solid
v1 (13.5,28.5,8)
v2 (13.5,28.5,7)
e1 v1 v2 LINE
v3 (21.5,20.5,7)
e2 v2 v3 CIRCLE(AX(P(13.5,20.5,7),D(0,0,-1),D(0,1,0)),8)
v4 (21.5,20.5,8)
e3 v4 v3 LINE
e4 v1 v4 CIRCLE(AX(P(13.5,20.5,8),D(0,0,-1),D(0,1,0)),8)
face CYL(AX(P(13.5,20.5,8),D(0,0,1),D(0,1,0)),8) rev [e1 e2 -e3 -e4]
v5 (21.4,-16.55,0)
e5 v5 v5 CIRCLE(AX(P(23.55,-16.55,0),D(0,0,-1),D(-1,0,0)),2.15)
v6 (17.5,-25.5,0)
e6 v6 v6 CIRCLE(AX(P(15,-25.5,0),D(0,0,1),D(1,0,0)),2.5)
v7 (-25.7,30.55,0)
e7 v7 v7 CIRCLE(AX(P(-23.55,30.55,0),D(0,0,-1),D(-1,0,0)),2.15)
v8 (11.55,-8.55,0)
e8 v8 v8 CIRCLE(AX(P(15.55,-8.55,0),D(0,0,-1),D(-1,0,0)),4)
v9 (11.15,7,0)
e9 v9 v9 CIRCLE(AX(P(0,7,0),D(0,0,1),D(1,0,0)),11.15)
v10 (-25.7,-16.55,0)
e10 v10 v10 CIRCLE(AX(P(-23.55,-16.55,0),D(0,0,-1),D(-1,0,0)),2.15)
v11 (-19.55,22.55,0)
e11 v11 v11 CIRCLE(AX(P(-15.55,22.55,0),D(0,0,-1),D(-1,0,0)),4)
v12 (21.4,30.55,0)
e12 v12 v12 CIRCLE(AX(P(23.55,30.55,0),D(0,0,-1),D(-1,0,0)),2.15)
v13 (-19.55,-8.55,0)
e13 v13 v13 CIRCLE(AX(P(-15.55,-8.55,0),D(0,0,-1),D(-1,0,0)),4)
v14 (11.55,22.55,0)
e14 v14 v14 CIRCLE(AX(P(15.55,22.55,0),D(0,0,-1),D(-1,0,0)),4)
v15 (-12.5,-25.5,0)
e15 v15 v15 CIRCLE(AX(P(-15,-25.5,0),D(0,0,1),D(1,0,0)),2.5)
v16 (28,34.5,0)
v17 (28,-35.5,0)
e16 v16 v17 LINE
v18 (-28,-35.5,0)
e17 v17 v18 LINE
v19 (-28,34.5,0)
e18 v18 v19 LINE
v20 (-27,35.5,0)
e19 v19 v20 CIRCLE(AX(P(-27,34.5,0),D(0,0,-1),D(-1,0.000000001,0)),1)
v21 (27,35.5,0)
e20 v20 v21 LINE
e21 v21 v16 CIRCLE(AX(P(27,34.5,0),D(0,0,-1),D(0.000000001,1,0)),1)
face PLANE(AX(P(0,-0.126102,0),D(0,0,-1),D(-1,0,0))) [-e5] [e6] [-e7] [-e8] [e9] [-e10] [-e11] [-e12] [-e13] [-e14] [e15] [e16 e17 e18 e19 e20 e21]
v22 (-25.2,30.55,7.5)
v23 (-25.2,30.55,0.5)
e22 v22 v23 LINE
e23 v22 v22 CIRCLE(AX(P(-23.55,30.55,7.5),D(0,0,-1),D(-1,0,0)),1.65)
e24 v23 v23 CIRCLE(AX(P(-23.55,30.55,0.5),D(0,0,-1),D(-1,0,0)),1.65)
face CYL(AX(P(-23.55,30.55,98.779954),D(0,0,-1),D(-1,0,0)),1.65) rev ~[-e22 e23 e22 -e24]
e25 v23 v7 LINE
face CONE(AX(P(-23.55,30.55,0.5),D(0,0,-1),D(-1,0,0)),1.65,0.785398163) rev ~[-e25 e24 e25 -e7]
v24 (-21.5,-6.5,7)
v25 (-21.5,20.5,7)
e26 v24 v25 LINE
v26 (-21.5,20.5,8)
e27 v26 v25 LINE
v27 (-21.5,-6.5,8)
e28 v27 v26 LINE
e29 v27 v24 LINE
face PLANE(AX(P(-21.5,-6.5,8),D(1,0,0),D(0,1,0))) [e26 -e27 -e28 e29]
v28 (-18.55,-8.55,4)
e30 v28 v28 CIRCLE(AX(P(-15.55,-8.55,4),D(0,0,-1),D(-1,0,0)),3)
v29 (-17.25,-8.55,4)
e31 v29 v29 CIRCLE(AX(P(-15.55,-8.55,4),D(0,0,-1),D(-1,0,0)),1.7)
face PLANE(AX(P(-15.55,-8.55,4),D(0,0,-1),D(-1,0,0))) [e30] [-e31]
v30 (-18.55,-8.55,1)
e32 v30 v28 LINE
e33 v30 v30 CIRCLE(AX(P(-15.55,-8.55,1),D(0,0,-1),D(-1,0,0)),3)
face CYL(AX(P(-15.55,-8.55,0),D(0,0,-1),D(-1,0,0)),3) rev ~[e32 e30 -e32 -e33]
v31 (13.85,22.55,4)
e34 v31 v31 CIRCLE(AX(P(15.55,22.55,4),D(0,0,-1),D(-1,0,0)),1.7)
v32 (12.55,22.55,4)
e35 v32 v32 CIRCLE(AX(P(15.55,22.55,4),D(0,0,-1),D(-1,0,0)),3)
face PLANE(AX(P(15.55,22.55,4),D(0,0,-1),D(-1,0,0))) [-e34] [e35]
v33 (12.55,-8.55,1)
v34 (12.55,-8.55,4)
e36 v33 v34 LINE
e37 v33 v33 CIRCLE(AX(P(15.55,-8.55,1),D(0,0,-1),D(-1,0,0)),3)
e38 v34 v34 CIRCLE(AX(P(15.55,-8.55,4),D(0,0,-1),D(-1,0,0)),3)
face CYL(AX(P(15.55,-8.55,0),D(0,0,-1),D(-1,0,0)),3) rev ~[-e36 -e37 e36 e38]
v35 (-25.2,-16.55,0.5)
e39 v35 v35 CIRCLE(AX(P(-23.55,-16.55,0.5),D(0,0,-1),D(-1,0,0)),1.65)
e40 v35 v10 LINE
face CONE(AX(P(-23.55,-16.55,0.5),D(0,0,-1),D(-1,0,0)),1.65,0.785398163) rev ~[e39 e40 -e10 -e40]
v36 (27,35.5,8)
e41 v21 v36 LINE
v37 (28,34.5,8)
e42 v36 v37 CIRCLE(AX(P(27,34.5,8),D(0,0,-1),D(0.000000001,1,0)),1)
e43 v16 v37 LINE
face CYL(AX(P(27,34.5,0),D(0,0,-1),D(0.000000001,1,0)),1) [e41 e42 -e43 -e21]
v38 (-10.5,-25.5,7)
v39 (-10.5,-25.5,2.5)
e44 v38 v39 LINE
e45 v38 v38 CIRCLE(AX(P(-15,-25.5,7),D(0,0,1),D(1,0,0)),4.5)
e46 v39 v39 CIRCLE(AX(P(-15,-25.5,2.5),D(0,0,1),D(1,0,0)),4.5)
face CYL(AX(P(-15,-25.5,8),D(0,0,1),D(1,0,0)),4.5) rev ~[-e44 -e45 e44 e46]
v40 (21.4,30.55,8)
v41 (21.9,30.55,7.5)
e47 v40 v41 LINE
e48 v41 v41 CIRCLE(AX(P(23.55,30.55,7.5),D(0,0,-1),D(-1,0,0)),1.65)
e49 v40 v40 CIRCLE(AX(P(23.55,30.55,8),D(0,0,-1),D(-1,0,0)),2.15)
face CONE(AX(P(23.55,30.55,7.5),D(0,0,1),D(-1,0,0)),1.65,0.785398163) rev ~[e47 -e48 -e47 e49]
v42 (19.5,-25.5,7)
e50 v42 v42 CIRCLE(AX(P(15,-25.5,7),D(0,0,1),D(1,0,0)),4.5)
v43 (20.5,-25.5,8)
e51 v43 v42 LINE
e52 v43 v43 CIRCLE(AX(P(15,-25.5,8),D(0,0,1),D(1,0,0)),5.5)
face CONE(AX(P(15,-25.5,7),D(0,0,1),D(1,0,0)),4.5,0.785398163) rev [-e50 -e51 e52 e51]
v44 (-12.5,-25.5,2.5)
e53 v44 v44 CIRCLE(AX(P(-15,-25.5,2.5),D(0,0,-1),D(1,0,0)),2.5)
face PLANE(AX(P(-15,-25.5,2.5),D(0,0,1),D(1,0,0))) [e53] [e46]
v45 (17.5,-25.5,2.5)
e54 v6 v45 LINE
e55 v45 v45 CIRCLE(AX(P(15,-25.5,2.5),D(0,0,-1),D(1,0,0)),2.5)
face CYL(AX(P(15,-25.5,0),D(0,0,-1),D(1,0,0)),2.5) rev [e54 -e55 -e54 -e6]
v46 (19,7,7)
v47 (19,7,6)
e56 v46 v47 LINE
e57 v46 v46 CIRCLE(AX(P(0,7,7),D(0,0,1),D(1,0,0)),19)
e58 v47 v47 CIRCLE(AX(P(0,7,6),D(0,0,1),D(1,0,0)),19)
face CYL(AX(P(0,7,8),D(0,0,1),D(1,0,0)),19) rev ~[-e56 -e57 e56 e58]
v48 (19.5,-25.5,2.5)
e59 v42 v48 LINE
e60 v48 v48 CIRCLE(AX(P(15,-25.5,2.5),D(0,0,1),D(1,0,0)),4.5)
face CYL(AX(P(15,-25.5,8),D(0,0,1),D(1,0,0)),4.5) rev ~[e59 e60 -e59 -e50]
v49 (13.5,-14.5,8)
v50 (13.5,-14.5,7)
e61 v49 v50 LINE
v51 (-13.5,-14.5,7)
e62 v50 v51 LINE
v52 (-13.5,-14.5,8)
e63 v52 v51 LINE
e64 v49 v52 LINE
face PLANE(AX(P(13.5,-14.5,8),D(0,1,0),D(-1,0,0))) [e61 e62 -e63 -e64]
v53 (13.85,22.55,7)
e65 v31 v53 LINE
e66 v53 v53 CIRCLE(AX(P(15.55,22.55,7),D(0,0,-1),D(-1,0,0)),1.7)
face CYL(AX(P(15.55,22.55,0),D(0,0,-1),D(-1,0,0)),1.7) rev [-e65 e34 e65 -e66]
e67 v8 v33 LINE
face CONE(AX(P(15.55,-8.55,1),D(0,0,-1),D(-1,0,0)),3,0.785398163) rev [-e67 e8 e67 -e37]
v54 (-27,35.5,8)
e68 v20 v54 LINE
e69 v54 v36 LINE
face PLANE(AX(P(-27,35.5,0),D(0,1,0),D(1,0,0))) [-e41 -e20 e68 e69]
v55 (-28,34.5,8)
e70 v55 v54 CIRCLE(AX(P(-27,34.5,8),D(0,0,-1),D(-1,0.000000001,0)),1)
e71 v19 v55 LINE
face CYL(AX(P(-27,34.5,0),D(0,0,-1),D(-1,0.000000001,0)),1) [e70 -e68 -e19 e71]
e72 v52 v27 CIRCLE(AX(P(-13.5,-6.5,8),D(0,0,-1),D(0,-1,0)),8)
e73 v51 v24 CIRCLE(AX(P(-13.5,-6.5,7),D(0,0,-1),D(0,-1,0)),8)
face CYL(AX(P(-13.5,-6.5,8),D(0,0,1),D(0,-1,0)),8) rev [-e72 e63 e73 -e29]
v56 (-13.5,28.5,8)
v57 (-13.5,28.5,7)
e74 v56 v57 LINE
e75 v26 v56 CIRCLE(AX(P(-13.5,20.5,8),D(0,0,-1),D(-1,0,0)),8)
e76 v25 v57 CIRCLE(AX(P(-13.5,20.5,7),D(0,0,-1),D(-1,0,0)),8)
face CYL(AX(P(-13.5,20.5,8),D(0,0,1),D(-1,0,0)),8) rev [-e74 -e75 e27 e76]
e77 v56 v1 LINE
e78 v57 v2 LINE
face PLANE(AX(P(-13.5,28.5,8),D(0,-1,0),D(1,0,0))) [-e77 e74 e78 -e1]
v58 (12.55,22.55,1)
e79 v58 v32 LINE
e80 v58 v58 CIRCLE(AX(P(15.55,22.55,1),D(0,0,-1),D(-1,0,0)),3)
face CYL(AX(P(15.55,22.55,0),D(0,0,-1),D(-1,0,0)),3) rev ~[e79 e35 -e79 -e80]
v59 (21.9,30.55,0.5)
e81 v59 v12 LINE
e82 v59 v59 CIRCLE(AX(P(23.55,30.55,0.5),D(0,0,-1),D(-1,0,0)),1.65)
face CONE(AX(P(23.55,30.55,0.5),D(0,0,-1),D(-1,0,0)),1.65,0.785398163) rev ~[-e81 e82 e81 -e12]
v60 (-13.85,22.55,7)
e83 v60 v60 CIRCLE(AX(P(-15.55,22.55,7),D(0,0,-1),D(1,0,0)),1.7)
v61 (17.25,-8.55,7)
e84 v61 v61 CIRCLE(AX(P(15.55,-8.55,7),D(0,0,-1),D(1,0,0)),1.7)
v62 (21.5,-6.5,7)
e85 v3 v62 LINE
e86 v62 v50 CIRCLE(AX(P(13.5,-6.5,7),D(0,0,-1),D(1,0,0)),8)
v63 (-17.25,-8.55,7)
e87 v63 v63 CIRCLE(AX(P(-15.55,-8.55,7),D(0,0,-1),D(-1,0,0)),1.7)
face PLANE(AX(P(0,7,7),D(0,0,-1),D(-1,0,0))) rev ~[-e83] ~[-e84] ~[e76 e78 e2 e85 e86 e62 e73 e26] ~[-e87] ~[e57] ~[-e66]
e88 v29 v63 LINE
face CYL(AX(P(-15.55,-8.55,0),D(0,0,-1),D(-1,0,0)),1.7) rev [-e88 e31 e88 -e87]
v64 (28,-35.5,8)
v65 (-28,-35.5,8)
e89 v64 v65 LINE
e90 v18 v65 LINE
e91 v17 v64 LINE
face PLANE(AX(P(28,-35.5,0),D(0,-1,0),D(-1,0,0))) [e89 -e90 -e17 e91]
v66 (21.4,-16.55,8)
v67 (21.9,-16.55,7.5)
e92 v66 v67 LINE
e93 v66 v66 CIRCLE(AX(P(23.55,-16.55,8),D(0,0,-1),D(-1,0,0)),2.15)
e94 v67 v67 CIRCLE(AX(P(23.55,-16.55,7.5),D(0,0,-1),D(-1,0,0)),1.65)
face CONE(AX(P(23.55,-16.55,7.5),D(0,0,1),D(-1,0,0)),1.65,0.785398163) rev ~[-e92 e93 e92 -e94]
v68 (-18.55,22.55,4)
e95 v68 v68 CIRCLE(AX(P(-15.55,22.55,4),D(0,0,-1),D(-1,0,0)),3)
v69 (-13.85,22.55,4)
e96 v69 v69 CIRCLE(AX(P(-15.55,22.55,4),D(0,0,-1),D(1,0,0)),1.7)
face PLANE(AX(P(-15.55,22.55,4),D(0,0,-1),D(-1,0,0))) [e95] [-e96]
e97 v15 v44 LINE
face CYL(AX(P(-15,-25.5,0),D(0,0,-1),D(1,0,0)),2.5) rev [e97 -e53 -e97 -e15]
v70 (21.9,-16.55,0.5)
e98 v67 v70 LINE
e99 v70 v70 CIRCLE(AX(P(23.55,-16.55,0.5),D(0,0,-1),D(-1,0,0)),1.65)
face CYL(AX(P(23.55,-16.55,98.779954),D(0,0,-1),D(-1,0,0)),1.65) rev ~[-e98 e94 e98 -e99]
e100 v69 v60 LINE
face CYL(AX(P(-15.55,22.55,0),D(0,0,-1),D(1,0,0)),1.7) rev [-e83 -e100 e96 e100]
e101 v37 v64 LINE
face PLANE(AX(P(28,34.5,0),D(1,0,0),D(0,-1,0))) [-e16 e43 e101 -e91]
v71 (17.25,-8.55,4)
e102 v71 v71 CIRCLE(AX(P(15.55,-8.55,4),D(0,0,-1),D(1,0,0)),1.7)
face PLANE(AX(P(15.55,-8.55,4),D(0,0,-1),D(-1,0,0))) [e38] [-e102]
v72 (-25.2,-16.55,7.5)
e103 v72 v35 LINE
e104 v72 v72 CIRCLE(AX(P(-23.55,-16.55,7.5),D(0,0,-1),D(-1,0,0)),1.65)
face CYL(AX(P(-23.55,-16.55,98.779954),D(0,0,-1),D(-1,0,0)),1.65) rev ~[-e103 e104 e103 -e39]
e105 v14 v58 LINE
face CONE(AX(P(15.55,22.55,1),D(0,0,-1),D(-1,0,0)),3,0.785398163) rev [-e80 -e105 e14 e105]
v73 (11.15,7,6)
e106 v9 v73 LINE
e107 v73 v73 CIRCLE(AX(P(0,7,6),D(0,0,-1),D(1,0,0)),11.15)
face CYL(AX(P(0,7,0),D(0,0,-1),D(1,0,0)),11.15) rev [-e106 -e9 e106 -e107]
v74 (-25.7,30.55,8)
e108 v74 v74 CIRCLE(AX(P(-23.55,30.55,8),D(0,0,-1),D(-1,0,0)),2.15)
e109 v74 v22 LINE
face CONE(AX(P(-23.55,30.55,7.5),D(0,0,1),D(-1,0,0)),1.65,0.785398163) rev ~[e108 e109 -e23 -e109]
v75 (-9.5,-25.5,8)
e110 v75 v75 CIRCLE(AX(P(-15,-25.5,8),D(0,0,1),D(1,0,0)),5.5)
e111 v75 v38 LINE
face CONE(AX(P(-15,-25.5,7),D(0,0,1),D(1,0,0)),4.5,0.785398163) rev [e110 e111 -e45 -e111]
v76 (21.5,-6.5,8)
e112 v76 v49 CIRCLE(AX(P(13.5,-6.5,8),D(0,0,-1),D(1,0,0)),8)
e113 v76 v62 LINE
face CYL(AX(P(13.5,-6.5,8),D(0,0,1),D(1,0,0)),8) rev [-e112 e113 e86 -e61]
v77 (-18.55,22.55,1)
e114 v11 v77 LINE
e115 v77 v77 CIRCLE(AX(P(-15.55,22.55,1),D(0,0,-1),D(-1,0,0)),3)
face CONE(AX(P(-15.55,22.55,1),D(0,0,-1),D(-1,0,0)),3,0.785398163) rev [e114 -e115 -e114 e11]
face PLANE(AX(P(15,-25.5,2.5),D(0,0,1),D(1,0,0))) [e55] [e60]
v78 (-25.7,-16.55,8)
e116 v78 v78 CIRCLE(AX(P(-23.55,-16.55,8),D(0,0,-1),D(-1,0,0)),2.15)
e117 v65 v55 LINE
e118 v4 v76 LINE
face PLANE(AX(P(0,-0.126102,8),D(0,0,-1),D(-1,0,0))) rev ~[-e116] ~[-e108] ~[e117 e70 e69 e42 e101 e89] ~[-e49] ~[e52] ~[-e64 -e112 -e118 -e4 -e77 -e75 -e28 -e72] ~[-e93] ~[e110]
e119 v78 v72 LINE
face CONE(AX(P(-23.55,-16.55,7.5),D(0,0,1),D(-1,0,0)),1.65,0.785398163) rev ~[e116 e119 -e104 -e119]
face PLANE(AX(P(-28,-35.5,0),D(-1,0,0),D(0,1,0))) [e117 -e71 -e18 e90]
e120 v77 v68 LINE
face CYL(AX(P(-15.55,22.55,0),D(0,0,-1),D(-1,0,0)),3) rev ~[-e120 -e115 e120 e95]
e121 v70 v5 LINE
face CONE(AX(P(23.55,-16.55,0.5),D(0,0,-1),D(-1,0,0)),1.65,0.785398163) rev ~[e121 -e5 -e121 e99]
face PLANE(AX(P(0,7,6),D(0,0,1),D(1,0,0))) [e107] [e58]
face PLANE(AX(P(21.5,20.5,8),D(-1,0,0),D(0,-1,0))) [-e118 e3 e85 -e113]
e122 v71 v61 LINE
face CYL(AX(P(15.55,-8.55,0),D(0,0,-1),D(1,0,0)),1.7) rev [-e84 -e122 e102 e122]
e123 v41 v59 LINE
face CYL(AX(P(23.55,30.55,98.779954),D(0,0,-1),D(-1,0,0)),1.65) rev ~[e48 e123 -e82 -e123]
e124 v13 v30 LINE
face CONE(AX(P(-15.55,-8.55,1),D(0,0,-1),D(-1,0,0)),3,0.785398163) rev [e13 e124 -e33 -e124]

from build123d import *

# Parameters (mm, degrees)
SKETCH1_R           = 11.15
SKETCH1_R_2         = 1.7
SKETCH1_R_3         = 1
SKETCH1_R_4         = 2.5
BOSS_EXTRUDE1_DEPTH = 8
SKETCH2_R           = 4.5
CUT_EXTRUDE1_DEPTH  = 5.5
SKETCH3_R           = 3
CUT_EXTRUDE2_DEPTH  = 4
CHAMFER1_SIZE       = 1
CHAMFER2_SIZE       = 0.5
CHAMFER3_SIZE       = 0.5
SKETCH4_R           = 19
CUT_EXTRUDE3_DEPTH  = 2
CUT_EXTRUDE4_DEPTH  = 1
CHAMFER4_SIZE       = 1
M4_TAPPED_HOLE1_D   = 3.3
CHAMFER5_SIZE       = 0.5


with BuildPart() as part:
    # Sketch1 → Boss-Extrude1 (new body)
    with BuildSketch(Plane.XY):
        with BuildLine():
            Line((-27, 35.5), (27, 35.5))
            ThreePointArc((27, 35.5), (27.707106781, 35.207106781), (28, 34.5))
            Line((28, 34.5), (28, -35.5))
            Line((28, -35.5), (-28, -35.5))
            Line((-28, -35.5), (-28, 34.5))
            ThreePointArc((-28, 34.5), (-27.707106781, 35.207106781), (-27, 35.5))
        make_face()
        with Locations((0, 7)):
            Circle(SKETCH1_R, mode=Mode.SUBTRACT)
        with Locations((-15.55, 22.55)):
            Circle(SKETCH1_R_2, mode=Mode.SUBTRACT)
        with Locations((-23.55, 30.55)):
            Circle(SKETCH1_R_3, mode=Mode.SUBTRACT)
        with Locations(Location((23.55, 30.55, 0), (0, 0, 180))):
            Circle(SKETCH1_R_3, mode=Mode.SUBTRACT)
        with Locations(Location((15.55, 22.55, 0), (0, 0, 180))):
            Circle(SKETCH1_R_2, mode=Mode.SUBTRACT)
        with Locations(Location((-23.55, -16.55, 0), (0, 0, 180))):
            Circle(SKETCH1_R_3, mode=Mode.SUBTRACT)
        with Locations(Location((-15.55, -8.55, 0), (0, 0, 180))):
            Circle(SKETCH1_R_2, mode=Mode.SUBTRACT)
        with Locations((15.55, -8.55)):
            Circle(SKETCH1_R_2, mode=Mode.SUBTRACT)
        with Locations((23.55, -16.55)):
            Circle(SKETCH1_R_3, mode=Mode.SUBTRACT)
        with Locations((-15, -25.5)):
            Circle(SKETCH1_R_4, mode=Mode.SUBTRACT)
        with Locations((15, -25.5)):
            Circle(SKETCH1_R_4, mode=Mode.SUBTRACT)
    extrude(amount=BOSS_EXTRUDE1_DEPTH)

    # Sketch2 → Cut-Extrude1 (cut)
    with BuildSketch(Plane.XY.offset(8)):
        with Locations((-15, -25.5)):
            Circle(SKETCH2_R)
        with Locations((15, -25.5)):
            Circle(SKETCH2_R)
    extrude(amount=-CUT_EXTRUDE1_DEPTH, mode=Mode.SUBTRACT)

    # Sketch3 → Cut-Extrude2 (cut)
    with BuildSketch(Plane(origin=(0, 0, 0), x_dir=(-1, 0, 0), z_dir=(0, 0, -1))):
        with Locations((-15.55, 22.55)):
            Circle(SKETCH3_R)
        with Locations((15.55, 22.55)):
            Circle(SKETCH3_R)
        with Locations((-15.55, -8.55)):
            Circle(SKETCH3_R)
        with Locations((15.55, -8.55)):
            Circle(SKETCH3_R)
    extrude(amount=-CUT_EXTRUDE2_DEPTH, mode=Mode.SUBTRACT)

    # Chamfer1
    chamfer1_edges = [part.edges().sort_by_distance(p)[0] for p in [
        (18.55, 22.55, 0),
        (-12.55, 22.55, 0),
        (18.55, -8.55, 0),
        (-12.55, -8.55, 0),
    ]]
    chamfer(chamfer1_edges, length=CHAMFER1_SIZE)

    # Chamfer2
    chamfer2_edges = [part.edges().sort_by_distance(p)[0] for p in [
        (-24.55, 30.55, 0),
        (24.55, 30.55, 0),
        (-22.55, -16.55, 0),
        (22.55, -16.55, 0),
    ]]
    chamfer(chamfer2_edges, length=CHAMFER2_SIZE)

    # Chamfer3
    chamfer3_edges = [part.edges().sort_by_distance(p)[0] for p in [
        (-24.55, 30.55, 8),
        (24.55, 30.55, 8),
        (-22.55, -16.55, 8),
        (22.55, -16.55, 8),
    ]]
    chamfer(chamfer3_edges, length=CHAMFER3_SIZE)

    # Sketch4 → Cut-Extrude3 (cut)
    with BuildSketch(Plane.XY.offset(8)):
        with Locations((0, 7)):
            Circle(SKETCH4_R)
    extrude(amount=-CUT_EXTRUDE3_DEPTH, mode=Mode.SUBTRACT)

    # Sketch5 → Cut-Extrude4 (cut)
    with BuildSketch(Plane.XY.offset(8)):
        with BuildLine():
            Line((-13.5, 28.5), (13.5, 28.5))
            ThreePointArc((13.5, 28.5), (19.156854249, 26.156854249), (21.5, 20.5))
            Line((21.5, 20.5), (21.5, -6.5))
            ThreePointArc((21.5, -6.5), (19.156854249, -12.156854249), (13.5, -14.5))
            Line((13.5, -14.5), (-13.5, -14.5))
            ThreePointArc((-13.5, -14.5), (-19.156854249, -12.156854249), (-21.5, -6.5))
            Line((-21.5, -6.5), (-21.5, 20.5))
            ThreePointArc((-21.5, 20.5), (-19.156854249, 26.156854249), (-13.5, 28.5))
        make_face()
    extrude(amount=-CUT_EXTRUDE4_DEPTH, mode=Mode.SUBTRACT)

    # Chamfer4
    chamfer4_edges = [part.edges().sort_by_distance(p)[0] for p in [
        (-19.5, -25.5, 8),
        (10.5, -25.5, 8),
    ]]
    chamfer(chamfer4_edges, length=CHAMFER4_SIZE)

    # M4 Tapped Hole1 (through all)
    with Locations(Plane.XY.offset(8)):
        with Locations((-23.55, 30.55), (23.55, 30.55), (23.55, -16.55), (-23.55, -16.55)):
            Hole(M4_TAPPED_HOLE1_D / 2)

    # Chamfer5
    chamfer5_edges = [part.edges().sort_by_distance(p)[0] for p in [
        (-21.9, -16.55, 8),
        (-21.9, -16.55, 0),
        (25.2, -16.55, 8),
        (25.2, -16.55, 0),
        (25.2, 30.55, 8),
        (25.2, 30.55, 0),
        (-21.9, 30.55, 8),
        (-21.9, 30.55, 0),
    ]]
    chamfer(chamfer5_edges, length=CHAMFER5_SIZE)


solid = part.part
